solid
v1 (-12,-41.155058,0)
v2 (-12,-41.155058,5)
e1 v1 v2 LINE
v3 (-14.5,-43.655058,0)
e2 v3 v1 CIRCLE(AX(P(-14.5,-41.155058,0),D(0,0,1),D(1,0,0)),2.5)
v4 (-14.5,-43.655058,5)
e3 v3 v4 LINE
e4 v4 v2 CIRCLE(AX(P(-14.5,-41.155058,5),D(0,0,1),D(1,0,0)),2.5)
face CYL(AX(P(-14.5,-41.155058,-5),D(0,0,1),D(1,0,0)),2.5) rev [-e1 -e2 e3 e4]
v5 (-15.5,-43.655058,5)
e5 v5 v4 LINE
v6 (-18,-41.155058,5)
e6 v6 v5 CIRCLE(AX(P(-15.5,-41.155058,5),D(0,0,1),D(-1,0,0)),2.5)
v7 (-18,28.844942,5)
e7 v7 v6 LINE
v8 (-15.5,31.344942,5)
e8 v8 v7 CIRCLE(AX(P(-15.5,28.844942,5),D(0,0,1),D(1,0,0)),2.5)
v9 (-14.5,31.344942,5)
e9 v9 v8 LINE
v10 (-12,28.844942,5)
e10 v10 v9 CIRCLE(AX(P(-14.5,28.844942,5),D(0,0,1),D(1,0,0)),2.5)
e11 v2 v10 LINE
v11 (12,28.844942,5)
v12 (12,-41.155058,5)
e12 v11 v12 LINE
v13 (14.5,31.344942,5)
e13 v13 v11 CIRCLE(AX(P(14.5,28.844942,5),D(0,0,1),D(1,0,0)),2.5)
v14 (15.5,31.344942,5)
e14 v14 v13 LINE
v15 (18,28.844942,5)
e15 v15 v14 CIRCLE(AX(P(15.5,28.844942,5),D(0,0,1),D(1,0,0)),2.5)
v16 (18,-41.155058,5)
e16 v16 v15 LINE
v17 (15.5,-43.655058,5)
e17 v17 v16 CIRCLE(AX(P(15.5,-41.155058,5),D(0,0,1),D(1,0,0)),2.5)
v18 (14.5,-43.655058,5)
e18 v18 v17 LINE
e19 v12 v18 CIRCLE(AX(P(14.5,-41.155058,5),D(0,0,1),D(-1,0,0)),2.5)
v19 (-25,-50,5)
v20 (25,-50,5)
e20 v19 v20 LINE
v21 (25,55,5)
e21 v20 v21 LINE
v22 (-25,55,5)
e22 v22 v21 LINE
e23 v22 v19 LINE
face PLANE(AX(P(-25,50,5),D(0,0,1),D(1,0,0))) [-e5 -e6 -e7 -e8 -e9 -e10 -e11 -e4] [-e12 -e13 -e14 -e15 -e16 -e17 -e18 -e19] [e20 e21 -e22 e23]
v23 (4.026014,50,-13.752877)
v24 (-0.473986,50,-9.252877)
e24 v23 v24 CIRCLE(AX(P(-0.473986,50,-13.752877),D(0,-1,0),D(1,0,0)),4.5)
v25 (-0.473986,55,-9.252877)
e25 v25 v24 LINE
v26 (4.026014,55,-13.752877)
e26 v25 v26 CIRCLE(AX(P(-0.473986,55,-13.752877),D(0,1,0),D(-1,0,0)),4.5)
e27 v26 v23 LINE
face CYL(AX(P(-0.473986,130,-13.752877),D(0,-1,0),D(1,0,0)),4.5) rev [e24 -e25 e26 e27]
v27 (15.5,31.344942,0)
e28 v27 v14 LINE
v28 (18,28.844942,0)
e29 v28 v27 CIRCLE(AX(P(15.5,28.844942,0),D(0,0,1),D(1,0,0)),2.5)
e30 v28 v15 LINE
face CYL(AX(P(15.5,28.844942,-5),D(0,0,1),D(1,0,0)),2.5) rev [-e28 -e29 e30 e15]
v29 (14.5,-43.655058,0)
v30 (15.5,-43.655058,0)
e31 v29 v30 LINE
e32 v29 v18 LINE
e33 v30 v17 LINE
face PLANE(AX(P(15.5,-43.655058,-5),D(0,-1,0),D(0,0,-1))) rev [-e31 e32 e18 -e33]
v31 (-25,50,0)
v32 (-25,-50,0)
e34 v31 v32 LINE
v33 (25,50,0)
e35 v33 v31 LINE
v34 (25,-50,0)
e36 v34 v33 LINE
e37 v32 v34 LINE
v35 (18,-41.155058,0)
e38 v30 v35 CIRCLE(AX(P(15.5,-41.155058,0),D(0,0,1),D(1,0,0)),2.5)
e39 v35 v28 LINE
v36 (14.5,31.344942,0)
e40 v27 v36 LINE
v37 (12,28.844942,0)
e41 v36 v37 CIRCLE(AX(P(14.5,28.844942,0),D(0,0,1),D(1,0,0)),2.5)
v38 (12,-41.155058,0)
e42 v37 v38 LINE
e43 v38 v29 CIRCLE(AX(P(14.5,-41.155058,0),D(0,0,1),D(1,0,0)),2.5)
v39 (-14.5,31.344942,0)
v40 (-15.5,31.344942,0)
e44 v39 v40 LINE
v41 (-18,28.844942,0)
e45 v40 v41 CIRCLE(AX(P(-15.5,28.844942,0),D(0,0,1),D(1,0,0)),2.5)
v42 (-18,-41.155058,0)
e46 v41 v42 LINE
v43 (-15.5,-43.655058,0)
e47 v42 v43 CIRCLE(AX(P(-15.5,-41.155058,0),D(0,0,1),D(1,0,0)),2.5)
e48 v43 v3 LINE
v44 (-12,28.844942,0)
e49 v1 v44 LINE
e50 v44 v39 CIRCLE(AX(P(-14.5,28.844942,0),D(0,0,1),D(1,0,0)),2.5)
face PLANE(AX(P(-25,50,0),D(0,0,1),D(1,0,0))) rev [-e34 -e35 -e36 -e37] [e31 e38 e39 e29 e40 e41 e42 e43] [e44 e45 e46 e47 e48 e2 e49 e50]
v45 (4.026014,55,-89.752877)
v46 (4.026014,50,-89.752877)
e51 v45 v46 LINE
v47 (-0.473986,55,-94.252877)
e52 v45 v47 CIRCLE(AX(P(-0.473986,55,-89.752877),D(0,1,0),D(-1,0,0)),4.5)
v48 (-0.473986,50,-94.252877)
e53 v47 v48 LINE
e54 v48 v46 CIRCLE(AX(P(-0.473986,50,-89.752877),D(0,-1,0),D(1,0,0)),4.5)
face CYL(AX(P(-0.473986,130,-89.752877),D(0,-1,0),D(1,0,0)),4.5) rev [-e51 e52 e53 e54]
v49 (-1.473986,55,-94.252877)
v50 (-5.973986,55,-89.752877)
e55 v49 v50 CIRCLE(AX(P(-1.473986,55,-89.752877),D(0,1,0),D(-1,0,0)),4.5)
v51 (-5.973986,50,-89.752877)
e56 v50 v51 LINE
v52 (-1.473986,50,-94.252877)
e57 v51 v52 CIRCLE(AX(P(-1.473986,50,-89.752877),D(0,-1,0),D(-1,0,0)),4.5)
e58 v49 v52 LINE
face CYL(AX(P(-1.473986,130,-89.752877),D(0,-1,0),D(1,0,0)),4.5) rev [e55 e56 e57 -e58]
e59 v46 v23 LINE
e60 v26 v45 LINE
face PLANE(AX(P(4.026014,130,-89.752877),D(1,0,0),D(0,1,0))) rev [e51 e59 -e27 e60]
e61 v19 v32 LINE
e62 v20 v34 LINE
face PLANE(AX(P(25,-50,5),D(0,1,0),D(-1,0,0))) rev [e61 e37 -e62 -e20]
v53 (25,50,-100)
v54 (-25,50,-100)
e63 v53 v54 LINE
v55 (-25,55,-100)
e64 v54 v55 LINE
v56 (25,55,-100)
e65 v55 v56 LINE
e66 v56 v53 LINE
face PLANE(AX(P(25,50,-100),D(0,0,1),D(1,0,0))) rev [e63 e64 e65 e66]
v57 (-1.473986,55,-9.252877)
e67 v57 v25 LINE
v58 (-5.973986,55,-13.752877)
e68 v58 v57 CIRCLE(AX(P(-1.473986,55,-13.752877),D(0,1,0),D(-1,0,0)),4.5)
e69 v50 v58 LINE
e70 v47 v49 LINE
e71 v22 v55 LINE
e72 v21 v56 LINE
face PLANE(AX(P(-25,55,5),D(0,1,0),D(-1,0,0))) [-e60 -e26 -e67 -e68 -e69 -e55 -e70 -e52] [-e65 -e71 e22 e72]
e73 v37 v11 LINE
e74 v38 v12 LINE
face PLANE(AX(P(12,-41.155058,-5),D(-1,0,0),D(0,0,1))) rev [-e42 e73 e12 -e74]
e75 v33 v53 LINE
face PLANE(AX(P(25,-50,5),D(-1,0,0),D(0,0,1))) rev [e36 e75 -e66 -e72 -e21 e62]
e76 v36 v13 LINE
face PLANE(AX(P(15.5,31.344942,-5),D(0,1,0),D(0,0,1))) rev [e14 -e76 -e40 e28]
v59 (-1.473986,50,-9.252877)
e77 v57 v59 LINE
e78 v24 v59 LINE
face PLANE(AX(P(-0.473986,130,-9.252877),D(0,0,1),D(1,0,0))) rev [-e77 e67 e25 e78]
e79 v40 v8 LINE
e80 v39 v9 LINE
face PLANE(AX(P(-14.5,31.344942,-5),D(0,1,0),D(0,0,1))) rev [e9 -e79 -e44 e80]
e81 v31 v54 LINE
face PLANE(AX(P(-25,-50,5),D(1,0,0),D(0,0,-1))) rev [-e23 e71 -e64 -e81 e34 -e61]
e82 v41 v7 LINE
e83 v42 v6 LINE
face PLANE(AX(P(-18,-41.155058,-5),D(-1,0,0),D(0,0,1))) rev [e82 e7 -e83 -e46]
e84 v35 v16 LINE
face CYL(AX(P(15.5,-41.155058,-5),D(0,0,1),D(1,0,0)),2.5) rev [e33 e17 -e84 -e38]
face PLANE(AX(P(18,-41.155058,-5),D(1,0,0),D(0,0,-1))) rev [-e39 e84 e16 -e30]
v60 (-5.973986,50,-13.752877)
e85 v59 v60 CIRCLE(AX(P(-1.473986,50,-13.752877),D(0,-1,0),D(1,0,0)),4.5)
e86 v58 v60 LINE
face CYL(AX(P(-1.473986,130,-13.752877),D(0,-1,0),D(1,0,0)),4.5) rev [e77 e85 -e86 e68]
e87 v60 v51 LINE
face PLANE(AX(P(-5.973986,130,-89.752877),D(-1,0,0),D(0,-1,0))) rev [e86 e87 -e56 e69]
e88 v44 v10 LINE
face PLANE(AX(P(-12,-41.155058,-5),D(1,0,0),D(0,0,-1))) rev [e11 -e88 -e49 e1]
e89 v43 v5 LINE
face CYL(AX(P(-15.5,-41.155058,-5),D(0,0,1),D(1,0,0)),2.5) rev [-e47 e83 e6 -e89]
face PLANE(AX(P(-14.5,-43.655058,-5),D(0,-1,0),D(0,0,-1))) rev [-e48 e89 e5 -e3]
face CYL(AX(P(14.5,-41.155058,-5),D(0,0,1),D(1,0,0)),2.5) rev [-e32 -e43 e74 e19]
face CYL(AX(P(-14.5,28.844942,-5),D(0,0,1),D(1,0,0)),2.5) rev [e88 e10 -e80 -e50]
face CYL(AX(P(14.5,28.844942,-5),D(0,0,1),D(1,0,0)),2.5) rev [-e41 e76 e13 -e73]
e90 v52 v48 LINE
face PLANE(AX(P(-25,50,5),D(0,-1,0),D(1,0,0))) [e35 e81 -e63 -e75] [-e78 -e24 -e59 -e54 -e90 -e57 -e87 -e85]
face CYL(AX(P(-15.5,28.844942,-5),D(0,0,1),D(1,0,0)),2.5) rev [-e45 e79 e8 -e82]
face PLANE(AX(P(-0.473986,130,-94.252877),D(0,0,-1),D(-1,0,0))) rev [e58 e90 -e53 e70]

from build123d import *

# Parameters (mm, degrees)
SKETCH1_W                = 50
SKETCH1_H                = 100
BOSS_EXTRUDE1_DEPTH      = 5
CUT_EXTRUDE1_DEPTH       = 10
BOSS_EXTRUDE2_DEPTH      = 100
BOSS_EXTRUDE2_DEPTH_BACK = 5
SKETCH4_W                = 50
SKETCH4_H                = 5
CUT_EXTRUDE3_DEPTH       = 80


with BuildPart() as part:
    # Sketch1 → Boss-Extrude1 (new body)
    with BuildSketch(Plane.XY):
        Rectangle(SKETCH1_W, SKETCH1_H)
    extrude(amount=BOSS_EXTRUDE1_DEPTH)

    # Sketch2 → Cut-Extrude1 (cut)
    with BuildSketch(Plane.XY.offset(5)):
        with BuildLine():
            Line((-14.5, -43.655057898), (-15.5, -43.655057898))
            ThreePointArc((-15.5, -43.655057898), (-17.267766953, -42.922824851), (-18, -41.155057898))
            Line((-18, -41.155057898), (-18, 28.844942102))
            ThreePointArc((-18, 28.844942102), (-17.267766953, 30.612709055), (-15.5, 31.344942102))
            Line((-15.5, 31.344942102), (-14.5, 31.344942102))
            ThreePointArc((-14.5, 31.344942102), (-12.732233047, 30.612709055), (-12, 28.844942102))
            Line((-12, 28.844942102), (-12, -41.155057898))
            ThreePointArc((-12, -41.155057898), (-12.732233047, -42.922824851), (-14.5, -43.655057898))
        make_face()
        with BuildLine():
            Line((15.5, -43.655057898), (14.5, -43.655057898))
            ThreePointArc((14.5, -43.655057898), (12.732233047, -42.922824851), (12, -41.155057898))
            Line((12, -41.155057898), (12, 28.844942102))
            ThreePointArc((12, 28.844942102), (12.732233047, 30.612709055), (14.5, 31.344942102))
            Line((14.5, 31.344942102), (15.5, 31.344942102))
            ThreePointArc((15.5, 31.344942102), (17.267766953, 30.612709055), (18, 28.844942102))
            Line((18, 28.844942102), (18, -41.155057898))
            ThreePointArc((18, -41.155057898), (17.267766953, -42.922824851), (15.5, -43.655057898))
        make_face()
    extrude(amount=-CUT_EXTRUDE1_DEPTH, mode=Mode.SUBTRACT)

    # Sketch4 → Boss-Extrude2 (add, two sides: drawn at the far end of the back side and taken through both)
    with BuildSketch(Plane(origin=(0, 0, 0), x_dir=(-1, 0, 0), z_dir=(0, 0, -1)).offset(-BOSS_EXTRUDE2_DEPTH_BACK)):
        with Locations((0, 52.5)):
            Rectangle(SKETCH4_W, SKETCH4_H)
    extrude(amount=BOSS_EXTRUDE2_DEPTH + BOSS_EXTRUDE2_DEPTH_BACK)

    # Sketch5 → Cut-Extrude3 (cut)
    with BuildSketch(Plane.XZ.offset(-50)):
        with BuildLine():
            Line((-0.473985761, -94.252877225), (-1.473985761, -94.252877225))
            ThreePointArc((-1.473985761, -94.252877225), (-4.655966276, -92.934857741), (-5.973985761, -89.752877225))
            Line((-5.973985761, -89.752877225), (-5.973985761, -13.752877225))
            ThreePointArc((-5.973985761, -13.752877225), (-4.655966276, -10.57089671), (-1.473985761, -9.252877225))
            Line((-1.473985761, -9.252877225), (-0.473985761, -9.252877225))
            ThreePointArc((-0.473985761, -9.252877225), (2.707994755, -10.57089671), (4.026014239, -13.752877225))
            Line((4.026014239, -13.752877225), (4.026014239, -89.752877225))
            ThreePointArc((4.026014239, -89.752877225), (2.707994755, -92.934857741), (-0.473985761, -94.252877225))
        make_face()
    extrude(amount=-CUT_EXTRUDE3_DEPTH, mode=Mode.SUBTRACT)


solid = part.part
